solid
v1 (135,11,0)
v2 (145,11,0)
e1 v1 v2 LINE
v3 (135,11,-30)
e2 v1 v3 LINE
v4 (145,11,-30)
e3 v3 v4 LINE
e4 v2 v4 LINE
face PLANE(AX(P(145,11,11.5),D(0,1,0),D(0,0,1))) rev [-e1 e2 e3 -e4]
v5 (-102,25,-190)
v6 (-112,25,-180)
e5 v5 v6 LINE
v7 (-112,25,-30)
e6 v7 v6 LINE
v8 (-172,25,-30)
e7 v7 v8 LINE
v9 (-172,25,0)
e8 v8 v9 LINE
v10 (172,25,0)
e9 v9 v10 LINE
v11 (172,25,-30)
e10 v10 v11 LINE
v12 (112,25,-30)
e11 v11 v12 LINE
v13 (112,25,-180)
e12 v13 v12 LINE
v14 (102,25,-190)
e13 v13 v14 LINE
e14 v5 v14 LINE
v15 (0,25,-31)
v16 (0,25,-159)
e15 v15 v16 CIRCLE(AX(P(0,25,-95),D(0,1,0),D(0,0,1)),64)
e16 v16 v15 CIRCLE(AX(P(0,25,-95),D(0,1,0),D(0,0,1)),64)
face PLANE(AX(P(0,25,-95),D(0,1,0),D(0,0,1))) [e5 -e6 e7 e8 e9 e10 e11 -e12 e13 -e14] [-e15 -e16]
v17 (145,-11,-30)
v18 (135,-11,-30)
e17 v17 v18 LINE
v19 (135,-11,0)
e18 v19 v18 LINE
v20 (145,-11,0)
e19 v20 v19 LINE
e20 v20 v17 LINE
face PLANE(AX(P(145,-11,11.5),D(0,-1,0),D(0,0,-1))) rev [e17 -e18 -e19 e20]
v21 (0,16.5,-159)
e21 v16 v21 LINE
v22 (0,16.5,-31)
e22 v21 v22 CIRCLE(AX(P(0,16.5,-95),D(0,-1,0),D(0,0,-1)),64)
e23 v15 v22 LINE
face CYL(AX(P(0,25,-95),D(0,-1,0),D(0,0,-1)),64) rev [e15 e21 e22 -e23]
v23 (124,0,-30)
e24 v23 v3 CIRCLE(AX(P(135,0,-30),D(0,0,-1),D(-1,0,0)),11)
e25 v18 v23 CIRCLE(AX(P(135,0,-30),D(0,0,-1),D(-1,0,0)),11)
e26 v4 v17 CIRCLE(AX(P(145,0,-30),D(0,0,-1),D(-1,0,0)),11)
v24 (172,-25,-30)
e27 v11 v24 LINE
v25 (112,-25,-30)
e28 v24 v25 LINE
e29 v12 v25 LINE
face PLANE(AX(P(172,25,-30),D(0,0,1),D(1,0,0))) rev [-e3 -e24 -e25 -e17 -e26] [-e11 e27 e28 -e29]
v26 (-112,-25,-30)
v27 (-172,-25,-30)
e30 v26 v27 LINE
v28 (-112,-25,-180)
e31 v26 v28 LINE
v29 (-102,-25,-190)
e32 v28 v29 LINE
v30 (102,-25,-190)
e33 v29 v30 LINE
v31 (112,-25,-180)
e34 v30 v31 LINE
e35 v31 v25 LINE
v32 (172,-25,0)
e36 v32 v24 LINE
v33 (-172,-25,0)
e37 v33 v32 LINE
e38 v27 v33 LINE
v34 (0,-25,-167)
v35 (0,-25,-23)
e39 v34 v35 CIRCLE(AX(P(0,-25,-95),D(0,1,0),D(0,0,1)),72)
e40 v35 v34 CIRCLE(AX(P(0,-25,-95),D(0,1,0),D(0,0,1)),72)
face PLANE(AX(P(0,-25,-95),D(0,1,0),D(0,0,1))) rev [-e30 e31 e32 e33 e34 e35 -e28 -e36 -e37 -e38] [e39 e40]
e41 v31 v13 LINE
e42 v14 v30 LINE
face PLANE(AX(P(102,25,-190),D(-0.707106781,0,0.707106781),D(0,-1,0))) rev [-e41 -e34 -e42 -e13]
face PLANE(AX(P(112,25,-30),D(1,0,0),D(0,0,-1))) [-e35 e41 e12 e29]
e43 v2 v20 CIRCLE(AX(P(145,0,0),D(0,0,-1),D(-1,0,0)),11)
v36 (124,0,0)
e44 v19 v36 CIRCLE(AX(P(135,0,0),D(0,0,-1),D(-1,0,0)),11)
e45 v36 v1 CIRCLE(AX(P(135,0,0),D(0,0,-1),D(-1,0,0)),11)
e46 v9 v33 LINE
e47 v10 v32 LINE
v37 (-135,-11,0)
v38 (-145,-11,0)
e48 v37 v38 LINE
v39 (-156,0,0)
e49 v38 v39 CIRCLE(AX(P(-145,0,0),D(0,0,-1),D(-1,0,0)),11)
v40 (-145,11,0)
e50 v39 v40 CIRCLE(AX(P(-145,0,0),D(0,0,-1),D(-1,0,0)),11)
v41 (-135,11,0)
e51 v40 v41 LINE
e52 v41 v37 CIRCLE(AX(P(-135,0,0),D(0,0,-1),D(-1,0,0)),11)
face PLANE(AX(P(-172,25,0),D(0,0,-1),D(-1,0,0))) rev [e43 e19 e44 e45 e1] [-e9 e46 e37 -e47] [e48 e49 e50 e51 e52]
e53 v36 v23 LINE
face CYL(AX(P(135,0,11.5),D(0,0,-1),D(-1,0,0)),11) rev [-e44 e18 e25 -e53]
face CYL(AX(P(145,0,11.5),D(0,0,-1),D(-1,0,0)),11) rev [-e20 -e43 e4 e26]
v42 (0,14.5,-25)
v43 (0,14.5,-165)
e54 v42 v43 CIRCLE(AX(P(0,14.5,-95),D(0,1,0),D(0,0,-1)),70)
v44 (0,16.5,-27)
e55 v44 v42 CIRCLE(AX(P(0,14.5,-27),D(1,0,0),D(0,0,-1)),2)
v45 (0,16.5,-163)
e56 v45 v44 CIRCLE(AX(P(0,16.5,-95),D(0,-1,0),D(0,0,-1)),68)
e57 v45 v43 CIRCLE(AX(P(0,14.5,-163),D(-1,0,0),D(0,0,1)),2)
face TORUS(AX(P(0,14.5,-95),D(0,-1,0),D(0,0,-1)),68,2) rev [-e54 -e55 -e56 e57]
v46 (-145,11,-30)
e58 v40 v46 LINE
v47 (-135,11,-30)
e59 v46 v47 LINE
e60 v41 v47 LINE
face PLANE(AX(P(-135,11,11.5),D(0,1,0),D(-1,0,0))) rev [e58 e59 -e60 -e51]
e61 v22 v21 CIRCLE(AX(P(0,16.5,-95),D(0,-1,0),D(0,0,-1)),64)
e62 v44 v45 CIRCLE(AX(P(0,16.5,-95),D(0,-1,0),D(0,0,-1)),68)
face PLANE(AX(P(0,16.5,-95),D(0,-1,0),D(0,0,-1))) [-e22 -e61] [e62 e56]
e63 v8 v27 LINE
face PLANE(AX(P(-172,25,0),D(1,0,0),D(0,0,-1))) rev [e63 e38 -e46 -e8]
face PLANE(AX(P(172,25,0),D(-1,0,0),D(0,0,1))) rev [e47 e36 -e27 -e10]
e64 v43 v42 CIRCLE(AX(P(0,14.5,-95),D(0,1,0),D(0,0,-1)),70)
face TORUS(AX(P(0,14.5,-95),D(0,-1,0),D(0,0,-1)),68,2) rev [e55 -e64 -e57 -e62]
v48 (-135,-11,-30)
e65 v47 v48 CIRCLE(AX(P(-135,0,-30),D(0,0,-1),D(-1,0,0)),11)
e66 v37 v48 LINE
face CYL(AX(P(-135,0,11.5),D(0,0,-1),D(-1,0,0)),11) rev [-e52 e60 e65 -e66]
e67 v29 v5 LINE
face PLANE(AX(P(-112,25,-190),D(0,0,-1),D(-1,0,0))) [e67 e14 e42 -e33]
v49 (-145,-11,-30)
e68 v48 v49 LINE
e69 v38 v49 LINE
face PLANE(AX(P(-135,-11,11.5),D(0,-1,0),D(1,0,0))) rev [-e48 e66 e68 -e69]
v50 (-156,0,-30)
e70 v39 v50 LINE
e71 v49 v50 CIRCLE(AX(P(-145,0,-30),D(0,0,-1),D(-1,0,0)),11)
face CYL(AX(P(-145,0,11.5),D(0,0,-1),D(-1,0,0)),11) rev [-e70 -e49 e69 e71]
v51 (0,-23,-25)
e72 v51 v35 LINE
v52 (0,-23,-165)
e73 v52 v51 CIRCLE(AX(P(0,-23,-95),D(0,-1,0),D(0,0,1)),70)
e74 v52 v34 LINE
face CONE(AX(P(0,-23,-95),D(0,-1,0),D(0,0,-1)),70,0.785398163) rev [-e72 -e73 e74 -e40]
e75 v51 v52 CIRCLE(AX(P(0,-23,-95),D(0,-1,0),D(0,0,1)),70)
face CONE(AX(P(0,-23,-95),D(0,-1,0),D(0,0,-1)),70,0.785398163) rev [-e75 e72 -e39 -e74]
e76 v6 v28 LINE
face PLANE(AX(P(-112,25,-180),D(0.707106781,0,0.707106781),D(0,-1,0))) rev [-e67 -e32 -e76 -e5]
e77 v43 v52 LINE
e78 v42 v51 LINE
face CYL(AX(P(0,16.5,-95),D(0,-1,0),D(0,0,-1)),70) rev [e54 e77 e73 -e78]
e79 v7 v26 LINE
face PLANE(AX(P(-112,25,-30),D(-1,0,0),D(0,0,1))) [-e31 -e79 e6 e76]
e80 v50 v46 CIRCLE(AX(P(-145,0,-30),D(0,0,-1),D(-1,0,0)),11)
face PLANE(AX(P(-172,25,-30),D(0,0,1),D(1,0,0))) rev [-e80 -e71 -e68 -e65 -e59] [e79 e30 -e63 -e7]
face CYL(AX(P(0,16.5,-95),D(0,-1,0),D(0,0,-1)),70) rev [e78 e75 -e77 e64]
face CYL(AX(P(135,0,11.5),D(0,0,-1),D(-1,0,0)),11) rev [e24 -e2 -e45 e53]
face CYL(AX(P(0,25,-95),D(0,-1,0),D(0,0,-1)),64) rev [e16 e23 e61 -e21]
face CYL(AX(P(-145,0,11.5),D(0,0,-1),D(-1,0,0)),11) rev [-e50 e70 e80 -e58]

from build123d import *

# Parameters (mm, degrees)
SKETCH1_R           = 64
BOSS_EXTRUDE1_DEPTH = 25
SKETCH2_R           = 70
CUT_EXTRUDE1_DEPTH  = 41.5
CHAMFER1_SIZE       = 2
FILLET1_R           = 2
CUT_EXTRUDE2_DEPTH  = 41.5
BOSS_EXTRUDE2_START = -50
BOSS_EXTRUDE2_DEPTH = 50
CHAMFER2_SIZE       = 10


with BuildPart() as part:
    # Sketch1 → Boss-Extrude1 (new, symmetric)
    with BuildSketch(Plane(origin=(0, 0, 0), x_dir=(1, 0, 0), z_dir=(0, 1, 0))):
        with BuildLine():
            Line((-172, 0), (172, 0))
            Line((172, 0), (172, 30))
            Line((172, 30), (112, 30))
            Line((112, 30), (91.468409221, 116.66864358))
            ThreePointArc((91.468409221, 116.66864358), (0, 189), (-91.468409221, 116.66864358))
            Line((-91.468409221, 116.66864358), (-112, 30))
            Line((-112, 30), (-172, 30))
            Line((-172, 30), (-172, 0))
        make_face()
        with Locations(Location((0, 95, 0), (0, 0, 270))):
            Circle(SKETCH1_R, mode=Mode.SUBTRACT)
    extrude(amount=BOSS_EXTRUDE1_DEPTH, both=True)

    # Sketch2 → Cut-Extrude1 (cut)
    with BuildSketch(Plane.XZ.offset(25)):
        with Locations(Location((0, -95, 0), (0, 0, 270))):
            Circle(SKETCH2_R)
    extrude(amount=-CUT_EXTRUDE1_DEPTH, mode=Mode.SUBTRACT)

    # Chamfer1
    chamfer1_edges = [part.edges().sort_by_distance(p)[0] for p in [
        (0, -25, -25),
    ]]
    chamfer(chamfer1_edges, length=CHAMFER1_SIZE)

    # Fillet1
    fillet1_edges = [part.edges().sort_by_distance(p)[0] for p in [
        (0, 16.5, -25),
    ]]
    fillet(fillet1_edges, radius=FILLET1_R)

    # Sketch3 → Cut-Extrude2 (cut)
    with BuildSketch(Plane(origin=(0, 0, -30), x_dir=(-1, 0, 0), z_dir=(0, 0, -1))):
        with BuildLine():
            Line((135, 11), (145, 11))
            ThreePointArc((145, 11), (156, 0), (145, -11))
            Line((145, -11), (135, -11))
            ThreePointArc((135, -11), (124, 0), (135, 11))
        make_face()
        with BuildLine():
            Line((-145, 11), (-135, 11))
            ThreePointArc((-135, 11), (-124, 0), (-135, -11))
            Line((-135, -11), (-145, -11))
            ThreePointArc((-145, -11), (-156, 0), (-145, 11))
        make_face()
    extrude(amount=-CUT_EXTRUDE2_DEPTH, mode=Mode.SUBTRACT)

    # Sketch4 → Boss-Extrude2 (add)
    with BuildSketch(Plane.XZ.offset(25).offset(BOSS_EXTRUDE2_START)):
        with BuildLine():
            Line((-112, -30), (-112, -190))
            Line((-112, -190), (112, -190))
            Line((112, -190), (112, -30))
            Line((112, -30), (91.468409221, -116.66864358))
            ThreePointArc((91.468409221, -116.66864358), (0, -189), (-91.468409221, -116.66864358))
            Line((-91.468409221, -116.66864358), (-112, -30))
        make_face()
    extrude(amount=BOSS_EXTRUDE2_DEPTH)

    # Chamfer2
    chamfer2_edges = [part.edges().sort_by_distance(p)[0] for p in [
        (112, 0, -190),
        (-112, 0, -190),
    ]]
    chamfer(chamfer2_edges, length=CHAMFER2_SIZE)


solid = part.part
